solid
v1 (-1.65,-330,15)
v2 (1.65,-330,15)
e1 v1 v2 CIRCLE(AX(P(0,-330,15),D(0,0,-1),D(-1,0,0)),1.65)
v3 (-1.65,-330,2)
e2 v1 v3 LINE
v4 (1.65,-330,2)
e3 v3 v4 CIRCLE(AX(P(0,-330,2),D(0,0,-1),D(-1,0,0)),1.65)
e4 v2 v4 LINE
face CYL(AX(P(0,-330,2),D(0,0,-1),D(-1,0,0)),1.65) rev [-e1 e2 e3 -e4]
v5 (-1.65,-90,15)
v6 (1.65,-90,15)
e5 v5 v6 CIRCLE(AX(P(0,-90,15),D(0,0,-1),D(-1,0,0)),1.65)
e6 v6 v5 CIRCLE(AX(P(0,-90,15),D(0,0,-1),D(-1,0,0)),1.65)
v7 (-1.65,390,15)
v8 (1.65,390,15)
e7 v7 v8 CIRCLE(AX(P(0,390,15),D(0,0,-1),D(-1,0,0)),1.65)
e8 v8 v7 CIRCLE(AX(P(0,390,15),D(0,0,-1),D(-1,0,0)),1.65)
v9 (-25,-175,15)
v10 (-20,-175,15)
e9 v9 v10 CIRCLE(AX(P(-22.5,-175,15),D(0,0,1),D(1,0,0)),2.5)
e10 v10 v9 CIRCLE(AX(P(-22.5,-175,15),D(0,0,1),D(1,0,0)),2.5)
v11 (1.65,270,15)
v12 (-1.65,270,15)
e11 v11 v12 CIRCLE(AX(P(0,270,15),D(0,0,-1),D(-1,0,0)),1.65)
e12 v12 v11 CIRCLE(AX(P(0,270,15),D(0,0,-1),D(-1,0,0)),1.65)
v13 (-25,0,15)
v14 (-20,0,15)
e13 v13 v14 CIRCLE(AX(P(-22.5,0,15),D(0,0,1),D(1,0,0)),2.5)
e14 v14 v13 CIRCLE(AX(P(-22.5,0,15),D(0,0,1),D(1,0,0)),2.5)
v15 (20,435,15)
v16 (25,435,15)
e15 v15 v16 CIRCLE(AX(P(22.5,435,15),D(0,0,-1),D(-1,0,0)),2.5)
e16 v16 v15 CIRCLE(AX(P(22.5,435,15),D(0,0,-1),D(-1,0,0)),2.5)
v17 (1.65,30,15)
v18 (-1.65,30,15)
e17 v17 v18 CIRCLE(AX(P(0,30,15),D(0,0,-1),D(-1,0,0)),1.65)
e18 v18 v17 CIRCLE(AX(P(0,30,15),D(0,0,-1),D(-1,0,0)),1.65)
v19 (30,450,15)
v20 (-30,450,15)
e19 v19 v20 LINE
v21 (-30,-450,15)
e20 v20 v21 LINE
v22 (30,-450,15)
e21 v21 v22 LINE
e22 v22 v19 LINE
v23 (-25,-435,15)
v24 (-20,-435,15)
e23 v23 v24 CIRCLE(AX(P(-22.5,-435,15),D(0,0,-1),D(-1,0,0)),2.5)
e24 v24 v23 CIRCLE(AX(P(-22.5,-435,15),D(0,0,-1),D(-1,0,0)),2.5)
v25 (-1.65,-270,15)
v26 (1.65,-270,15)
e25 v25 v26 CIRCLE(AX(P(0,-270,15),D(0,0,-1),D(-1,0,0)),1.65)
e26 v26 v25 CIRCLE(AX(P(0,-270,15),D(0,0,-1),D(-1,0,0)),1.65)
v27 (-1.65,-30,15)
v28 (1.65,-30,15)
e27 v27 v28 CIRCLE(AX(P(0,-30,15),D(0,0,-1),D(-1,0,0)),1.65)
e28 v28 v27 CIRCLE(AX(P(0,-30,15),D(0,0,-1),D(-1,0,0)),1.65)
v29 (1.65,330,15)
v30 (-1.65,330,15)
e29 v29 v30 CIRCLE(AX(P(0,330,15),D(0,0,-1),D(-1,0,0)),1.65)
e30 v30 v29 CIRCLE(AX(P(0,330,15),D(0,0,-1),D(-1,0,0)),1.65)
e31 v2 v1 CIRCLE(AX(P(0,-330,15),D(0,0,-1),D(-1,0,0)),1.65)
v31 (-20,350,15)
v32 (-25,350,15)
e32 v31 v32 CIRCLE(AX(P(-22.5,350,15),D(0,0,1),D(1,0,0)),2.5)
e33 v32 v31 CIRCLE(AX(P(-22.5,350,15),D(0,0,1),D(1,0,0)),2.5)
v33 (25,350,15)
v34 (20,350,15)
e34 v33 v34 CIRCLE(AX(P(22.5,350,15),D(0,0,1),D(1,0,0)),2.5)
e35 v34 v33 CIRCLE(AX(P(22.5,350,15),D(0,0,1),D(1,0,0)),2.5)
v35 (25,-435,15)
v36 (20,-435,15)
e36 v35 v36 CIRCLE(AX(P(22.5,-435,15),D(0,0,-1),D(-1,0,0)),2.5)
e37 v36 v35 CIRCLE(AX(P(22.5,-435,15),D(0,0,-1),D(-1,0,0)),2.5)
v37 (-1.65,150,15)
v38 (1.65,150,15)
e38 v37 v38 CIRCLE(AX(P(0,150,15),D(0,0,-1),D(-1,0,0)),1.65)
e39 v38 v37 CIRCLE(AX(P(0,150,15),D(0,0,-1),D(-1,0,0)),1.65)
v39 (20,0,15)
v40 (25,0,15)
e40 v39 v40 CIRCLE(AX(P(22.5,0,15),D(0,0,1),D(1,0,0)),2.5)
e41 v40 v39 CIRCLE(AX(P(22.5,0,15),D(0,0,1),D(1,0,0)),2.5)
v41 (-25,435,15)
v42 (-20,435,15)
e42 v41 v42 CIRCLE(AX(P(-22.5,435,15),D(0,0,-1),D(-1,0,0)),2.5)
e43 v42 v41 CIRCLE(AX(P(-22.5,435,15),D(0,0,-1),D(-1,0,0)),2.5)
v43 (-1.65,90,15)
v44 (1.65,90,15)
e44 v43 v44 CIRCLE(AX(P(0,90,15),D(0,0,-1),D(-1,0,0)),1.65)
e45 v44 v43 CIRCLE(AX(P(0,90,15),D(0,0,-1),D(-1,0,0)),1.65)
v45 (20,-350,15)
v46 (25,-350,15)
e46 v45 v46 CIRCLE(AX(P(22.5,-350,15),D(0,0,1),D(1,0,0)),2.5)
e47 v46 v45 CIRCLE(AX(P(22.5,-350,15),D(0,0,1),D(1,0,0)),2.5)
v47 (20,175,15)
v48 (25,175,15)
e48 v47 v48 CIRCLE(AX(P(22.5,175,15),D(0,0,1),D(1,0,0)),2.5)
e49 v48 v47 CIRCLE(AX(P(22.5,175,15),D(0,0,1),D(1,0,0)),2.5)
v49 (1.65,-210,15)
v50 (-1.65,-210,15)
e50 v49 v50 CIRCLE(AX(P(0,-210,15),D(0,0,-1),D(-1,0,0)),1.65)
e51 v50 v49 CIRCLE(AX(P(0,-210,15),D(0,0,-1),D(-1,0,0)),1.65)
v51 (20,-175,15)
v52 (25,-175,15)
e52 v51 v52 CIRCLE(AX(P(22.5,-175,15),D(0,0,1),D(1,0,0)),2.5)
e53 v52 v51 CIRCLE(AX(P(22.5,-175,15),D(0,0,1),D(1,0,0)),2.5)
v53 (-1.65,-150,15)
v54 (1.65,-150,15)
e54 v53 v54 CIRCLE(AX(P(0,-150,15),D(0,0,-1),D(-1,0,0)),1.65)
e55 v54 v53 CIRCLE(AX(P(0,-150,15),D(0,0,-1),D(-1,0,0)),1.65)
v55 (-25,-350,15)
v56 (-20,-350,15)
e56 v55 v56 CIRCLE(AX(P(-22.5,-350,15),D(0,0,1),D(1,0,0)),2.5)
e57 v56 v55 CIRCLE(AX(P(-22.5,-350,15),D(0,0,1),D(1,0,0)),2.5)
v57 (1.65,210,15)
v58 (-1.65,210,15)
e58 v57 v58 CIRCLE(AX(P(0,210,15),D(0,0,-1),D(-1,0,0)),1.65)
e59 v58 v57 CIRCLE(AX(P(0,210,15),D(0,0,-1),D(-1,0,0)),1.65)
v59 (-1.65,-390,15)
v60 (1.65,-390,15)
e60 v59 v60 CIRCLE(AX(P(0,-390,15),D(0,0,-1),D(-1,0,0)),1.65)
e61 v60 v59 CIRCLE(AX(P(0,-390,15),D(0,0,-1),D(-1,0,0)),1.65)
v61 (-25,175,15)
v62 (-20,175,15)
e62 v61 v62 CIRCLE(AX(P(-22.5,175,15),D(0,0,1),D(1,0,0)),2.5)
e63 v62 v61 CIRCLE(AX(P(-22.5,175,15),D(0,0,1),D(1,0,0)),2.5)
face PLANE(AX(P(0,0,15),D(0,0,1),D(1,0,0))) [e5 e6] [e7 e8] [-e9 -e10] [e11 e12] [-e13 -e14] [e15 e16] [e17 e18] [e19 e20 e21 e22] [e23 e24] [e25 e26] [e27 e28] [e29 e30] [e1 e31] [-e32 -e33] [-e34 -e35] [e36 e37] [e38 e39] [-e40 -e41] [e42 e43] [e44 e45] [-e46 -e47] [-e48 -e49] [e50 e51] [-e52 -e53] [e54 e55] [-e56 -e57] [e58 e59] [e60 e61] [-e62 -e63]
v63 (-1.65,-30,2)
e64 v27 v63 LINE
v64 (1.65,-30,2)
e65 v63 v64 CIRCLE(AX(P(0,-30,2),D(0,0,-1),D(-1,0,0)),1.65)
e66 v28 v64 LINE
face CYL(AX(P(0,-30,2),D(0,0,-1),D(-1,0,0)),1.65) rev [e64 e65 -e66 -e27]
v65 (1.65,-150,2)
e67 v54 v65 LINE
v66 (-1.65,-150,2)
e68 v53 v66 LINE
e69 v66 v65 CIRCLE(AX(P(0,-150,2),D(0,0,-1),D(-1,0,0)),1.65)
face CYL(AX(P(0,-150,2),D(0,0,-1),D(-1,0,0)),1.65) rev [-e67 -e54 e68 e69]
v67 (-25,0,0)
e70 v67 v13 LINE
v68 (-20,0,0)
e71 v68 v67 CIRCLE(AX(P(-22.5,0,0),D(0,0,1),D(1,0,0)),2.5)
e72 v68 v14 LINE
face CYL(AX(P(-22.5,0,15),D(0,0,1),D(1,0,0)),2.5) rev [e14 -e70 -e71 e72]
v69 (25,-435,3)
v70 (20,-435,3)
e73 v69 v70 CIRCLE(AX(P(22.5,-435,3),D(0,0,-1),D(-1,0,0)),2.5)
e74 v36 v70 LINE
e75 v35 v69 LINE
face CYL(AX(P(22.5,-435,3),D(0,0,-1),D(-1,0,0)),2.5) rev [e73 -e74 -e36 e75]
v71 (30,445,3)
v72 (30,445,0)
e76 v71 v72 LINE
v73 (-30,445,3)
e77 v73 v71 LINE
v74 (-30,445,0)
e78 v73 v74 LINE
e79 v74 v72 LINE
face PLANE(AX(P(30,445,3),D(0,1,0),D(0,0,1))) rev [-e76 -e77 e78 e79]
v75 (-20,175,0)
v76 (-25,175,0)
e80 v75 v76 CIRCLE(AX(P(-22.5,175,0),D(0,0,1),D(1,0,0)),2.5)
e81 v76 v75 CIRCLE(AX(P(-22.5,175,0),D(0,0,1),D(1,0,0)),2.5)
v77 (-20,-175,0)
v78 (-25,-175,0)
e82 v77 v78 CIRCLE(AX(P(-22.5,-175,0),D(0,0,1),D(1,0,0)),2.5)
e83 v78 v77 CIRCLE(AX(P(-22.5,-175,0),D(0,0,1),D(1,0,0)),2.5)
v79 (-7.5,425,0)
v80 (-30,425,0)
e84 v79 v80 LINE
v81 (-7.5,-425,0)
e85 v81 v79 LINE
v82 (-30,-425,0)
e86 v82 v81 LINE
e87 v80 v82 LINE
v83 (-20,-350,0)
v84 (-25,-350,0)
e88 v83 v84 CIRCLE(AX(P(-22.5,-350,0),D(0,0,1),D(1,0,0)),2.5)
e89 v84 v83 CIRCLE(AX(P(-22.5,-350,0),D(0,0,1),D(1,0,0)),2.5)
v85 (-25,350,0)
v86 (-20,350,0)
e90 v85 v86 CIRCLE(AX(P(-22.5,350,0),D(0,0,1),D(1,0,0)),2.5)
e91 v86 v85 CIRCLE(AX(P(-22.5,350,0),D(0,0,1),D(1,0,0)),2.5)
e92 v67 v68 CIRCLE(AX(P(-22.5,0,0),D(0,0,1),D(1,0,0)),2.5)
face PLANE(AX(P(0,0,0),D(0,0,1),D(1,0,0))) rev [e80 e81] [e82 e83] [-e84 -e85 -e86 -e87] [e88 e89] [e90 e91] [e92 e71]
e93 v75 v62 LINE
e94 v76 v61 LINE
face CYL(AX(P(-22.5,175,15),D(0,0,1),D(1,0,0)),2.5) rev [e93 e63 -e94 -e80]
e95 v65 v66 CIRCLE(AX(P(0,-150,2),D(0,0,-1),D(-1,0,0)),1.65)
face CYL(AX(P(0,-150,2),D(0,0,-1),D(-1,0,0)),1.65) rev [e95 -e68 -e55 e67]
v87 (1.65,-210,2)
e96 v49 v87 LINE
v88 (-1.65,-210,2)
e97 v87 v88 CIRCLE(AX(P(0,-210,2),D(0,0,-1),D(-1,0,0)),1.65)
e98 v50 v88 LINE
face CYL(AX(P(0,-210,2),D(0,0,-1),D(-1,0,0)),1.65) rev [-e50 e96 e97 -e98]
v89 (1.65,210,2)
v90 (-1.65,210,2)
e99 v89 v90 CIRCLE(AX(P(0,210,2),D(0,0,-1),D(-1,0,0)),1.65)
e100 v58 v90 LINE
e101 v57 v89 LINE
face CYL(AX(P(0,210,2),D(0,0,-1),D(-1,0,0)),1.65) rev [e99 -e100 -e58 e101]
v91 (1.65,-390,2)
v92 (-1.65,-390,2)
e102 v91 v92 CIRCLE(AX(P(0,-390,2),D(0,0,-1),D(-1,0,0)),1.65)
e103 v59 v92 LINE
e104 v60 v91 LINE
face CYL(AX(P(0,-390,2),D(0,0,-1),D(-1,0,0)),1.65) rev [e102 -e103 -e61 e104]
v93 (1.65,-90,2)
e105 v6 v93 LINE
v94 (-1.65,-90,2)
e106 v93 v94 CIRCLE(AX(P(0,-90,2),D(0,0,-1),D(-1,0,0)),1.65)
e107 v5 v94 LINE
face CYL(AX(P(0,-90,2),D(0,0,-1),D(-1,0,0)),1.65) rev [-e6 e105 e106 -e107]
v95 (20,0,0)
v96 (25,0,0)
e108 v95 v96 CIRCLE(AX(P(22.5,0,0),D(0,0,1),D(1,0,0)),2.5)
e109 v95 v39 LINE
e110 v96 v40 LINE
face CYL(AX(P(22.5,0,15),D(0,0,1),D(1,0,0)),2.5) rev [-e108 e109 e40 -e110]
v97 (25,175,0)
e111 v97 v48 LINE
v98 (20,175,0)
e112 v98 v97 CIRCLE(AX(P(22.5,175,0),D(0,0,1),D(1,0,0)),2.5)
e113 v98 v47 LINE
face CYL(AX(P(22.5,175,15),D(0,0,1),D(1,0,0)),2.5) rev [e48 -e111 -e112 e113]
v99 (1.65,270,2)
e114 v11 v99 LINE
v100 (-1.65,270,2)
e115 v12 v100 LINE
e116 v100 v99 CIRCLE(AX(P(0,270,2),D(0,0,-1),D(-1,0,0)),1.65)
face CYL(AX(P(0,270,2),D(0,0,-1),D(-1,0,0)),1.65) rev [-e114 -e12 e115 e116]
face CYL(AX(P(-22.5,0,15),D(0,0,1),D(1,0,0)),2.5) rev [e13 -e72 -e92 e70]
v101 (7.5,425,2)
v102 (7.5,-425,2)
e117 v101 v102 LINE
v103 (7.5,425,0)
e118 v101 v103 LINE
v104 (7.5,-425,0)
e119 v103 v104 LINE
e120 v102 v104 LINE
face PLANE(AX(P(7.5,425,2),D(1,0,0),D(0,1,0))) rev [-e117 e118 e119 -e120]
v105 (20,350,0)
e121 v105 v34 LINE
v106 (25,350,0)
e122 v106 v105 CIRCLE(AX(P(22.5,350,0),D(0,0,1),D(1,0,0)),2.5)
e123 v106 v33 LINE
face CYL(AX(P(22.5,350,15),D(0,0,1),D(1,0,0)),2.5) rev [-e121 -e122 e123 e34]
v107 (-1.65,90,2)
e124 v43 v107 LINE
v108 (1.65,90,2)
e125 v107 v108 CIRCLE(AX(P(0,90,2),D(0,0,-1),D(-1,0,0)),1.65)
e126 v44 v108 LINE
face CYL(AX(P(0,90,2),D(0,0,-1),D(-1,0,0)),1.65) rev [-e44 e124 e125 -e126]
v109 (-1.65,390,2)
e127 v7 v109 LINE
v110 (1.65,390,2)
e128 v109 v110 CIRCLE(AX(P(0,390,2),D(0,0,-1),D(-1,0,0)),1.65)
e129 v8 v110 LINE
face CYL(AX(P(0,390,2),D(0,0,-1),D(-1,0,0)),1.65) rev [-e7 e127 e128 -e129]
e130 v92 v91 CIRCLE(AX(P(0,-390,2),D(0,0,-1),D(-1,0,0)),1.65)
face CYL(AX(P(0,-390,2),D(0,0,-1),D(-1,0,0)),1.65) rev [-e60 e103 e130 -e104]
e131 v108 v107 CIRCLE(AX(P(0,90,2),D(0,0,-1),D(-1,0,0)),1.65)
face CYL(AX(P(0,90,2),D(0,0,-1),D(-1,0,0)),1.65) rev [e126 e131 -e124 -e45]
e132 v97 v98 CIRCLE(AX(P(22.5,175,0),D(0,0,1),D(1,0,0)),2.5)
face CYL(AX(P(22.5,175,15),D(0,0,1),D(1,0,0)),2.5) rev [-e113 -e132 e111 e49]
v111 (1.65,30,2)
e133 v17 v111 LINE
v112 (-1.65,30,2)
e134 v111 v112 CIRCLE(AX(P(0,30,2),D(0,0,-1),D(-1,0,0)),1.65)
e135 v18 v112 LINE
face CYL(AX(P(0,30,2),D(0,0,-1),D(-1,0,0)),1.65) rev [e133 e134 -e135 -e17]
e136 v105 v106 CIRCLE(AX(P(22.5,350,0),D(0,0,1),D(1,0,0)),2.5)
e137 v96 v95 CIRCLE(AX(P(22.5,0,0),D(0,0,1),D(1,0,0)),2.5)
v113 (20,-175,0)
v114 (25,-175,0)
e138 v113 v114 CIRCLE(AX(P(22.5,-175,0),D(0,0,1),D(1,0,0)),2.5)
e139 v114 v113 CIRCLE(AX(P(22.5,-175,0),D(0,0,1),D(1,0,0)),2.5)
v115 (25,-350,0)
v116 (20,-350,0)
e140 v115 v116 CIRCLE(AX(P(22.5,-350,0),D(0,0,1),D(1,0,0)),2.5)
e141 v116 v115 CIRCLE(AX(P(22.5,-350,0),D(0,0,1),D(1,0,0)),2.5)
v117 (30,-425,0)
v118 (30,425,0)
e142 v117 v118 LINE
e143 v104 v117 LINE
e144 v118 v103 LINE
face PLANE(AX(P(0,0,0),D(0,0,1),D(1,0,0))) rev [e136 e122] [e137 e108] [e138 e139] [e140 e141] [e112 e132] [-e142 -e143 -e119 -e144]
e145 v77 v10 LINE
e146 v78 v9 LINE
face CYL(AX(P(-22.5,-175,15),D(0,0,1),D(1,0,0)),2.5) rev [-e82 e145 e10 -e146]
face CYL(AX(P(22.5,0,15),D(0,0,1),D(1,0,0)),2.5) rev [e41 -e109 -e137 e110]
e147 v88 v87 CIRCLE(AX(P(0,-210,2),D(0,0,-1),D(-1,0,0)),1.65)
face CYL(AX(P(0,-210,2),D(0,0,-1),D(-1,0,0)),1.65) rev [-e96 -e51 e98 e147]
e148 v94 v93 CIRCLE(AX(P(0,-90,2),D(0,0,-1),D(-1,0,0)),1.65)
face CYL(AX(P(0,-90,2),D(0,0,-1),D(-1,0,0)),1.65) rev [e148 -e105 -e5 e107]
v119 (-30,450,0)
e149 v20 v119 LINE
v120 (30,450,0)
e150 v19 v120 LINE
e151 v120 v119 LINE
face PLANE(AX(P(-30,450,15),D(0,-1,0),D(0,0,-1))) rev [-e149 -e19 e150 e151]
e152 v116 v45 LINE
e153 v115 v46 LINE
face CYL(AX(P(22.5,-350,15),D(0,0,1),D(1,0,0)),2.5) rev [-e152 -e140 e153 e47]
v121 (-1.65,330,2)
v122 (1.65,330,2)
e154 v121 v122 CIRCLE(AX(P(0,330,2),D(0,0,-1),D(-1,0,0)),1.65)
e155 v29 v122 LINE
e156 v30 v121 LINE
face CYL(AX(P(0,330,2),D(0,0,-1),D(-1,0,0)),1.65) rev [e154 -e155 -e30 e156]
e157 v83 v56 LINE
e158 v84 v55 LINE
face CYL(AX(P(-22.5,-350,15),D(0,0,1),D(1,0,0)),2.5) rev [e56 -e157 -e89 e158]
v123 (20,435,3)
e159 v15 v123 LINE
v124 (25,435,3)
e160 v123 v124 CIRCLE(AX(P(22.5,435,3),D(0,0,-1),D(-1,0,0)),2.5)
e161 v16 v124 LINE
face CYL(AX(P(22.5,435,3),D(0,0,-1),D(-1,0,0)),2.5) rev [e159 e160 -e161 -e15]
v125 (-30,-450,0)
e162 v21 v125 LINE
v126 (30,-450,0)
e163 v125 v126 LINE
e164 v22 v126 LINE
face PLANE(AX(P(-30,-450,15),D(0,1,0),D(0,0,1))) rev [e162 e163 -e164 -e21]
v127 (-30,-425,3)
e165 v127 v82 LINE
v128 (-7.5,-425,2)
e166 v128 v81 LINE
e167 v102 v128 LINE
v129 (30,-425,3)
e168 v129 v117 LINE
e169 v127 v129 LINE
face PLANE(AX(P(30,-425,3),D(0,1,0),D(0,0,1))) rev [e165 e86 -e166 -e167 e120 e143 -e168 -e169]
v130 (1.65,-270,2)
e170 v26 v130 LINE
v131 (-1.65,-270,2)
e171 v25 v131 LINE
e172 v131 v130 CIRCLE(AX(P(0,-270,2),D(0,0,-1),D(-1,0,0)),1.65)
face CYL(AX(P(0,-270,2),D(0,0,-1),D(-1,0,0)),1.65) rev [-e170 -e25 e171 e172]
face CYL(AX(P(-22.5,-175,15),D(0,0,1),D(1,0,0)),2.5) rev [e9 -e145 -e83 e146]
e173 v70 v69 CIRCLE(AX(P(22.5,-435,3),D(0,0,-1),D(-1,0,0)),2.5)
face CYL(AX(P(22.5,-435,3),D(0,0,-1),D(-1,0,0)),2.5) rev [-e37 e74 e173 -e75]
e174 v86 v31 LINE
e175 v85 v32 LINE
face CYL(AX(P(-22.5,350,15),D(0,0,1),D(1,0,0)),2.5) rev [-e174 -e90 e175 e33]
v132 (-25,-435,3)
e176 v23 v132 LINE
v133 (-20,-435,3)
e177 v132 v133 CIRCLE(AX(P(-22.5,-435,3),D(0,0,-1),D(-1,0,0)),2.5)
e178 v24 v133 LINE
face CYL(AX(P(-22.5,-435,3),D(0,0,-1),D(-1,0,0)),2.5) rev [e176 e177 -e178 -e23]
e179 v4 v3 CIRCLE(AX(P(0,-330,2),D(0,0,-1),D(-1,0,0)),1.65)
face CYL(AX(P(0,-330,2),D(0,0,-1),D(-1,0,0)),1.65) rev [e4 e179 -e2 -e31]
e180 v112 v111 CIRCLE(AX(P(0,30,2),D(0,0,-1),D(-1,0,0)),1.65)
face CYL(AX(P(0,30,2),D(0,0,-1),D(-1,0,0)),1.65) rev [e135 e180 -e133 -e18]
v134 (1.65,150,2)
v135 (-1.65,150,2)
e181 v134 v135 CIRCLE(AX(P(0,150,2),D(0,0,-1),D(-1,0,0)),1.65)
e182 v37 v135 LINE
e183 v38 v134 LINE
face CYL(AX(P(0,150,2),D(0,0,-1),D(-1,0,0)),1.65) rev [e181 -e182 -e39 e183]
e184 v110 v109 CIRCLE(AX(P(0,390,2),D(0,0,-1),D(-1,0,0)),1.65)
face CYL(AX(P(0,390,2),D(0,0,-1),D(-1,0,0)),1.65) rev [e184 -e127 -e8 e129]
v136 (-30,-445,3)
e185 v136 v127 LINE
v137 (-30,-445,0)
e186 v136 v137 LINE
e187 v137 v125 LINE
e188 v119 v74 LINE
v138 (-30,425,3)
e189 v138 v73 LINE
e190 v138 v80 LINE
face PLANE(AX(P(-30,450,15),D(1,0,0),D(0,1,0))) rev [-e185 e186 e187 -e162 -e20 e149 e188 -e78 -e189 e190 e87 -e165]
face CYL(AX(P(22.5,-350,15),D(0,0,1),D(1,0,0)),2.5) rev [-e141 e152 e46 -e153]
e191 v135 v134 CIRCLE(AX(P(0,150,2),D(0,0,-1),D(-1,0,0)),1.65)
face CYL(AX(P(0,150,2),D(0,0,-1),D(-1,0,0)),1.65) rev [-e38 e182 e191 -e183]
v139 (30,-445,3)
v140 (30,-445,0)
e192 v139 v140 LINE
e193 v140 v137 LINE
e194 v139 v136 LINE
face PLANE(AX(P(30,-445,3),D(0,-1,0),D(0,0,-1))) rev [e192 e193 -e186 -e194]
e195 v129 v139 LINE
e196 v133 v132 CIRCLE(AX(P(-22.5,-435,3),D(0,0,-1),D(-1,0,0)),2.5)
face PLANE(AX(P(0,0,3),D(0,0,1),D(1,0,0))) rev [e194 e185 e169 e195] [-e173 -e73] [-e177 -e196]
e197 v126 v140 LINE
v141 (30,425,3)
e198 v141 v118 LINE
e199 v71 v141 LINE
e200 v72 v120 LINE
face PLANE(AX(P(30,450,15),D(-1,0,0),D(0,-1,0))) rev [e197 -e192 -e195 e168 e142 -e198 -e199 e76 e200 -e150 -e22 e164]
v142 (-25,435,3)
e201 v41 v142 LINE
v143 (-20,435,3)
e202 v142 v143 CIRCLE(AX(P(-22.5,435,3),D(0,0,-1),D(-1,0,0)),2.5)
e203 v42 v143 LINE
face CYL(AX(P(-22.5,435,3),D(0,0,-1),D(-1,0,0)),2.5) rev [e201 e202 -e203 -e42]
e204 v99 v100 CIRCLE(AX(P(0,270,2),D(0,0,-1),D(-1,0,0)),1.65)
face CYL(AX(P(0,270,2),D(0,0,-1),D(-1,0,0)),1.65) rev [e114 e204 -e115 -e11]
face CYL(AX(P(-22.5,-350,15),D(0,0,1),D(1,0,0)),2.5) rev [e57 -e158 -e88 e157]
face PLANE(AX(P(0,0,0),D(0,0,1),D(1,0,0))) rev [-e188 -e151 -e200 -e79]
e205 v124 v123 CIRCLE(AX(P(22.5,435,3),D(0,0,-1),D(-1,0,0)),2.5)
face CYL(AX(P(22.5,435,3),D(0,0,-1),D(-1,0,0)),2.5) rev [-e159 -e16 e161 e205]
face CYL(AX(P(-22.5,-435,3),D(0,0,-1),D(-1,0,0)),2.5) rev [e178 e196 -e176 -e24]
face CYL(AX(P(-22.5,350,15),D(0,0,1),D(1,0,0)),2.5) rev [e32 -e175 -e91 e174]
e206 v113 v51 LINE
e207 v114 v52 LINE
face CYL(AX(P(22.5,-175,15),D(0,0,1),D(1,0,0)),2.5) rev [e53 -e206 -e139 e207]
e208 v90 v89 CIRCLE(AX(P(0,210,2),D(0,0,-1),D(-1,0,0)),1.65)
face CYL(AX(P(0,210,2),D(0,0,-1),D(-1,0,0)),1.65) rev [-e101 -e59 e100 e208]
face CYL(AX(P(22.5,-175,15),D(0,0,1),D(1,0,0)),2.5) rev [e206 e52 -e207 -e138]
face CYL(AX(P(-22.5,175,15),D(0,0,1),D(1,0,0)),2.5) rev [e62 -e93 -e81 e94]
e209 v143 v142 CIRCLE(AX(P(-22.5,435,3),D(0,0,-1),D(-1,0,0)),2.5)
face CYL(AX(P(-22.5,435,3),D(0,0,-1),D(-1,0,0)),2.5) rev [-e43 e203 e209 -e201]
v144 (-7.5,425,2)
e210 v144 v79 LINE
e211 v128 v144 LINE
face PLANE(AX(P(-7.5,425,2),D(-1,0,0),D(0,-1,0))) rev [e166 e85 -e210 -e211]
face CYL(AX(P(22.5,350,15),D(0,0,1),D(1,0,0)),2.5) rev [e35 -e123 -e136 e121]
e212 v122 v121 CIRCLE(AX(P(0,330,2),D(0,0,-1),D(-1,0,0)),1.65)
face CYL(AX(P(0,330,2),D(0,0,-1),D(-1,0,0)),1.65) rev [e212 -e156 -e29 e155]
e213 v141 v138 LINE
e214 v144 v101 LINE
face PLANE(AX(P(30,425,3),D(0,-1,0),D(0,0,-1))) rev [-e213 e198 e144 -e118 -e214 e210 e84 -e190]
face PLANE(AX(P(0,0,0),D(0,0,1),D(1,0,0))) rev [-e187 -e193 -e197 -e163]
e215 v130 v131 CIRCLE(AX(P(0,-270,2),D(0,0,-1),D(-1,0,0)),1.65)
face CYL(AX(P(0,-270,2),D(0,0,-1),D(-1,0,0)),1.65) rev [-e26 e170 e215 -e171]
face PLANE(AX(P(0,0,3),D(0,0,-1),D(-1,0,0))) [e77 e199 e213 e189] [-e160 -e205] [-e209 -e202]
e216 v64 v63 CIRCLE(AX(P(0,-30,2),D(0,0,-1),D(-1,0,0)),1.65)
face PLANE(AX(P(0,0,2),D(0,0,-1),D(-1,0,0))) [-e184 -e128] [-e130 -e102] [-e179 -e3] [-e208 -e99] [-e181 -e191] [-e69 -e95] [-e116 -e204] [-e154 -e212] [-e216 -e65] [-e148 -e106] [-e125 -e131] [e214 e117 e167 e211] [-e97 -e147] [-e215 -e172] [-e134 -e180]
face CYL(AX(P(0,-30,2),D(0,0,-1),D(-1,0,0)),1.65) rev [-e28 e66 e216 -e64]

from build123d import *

# Parameters (mm, degrees)
SKETCH1_W           = 60
SKETCH1_H           = 900
BOSS_EXTRUDE1_DEPTH = 15
SKETCH5_W           = 60
SKETCH5_H           = 20
CUT_EXTRUDE2_DEPTH  = 3
SKETCH7_W           = 15
SKETCH7_H           = 850
CUT_EXTRUDE3_DEPTH  = 2
M4_TAPPED_HOLE1_D   = 3.3
LPATTERN1_COUNT     = 14
LPATTERN1_PITCH     = 60
M6_TAPPED_HOLE1_D   = 5
M6_TAPPED_HOLE2_D   = 5
LPATTERN2_COUNT     = 3
LPATTERN2_PITCH     = 175
LPATTERN2_COL_COUNT = 3
LPATTERN2_COL_PITCH = 175


with BuildPart() as part:
    # Sketch1 → Boss-Extrude1 (new body)
    with BuildSketch(Plane.XY):
        Rectangle(SKETCH1_W, SKETCH1_H)
    extrude(amount=BOSS_EXTRUDE1_DEPTH)

    # Sketch5 → Cut-Extrude2 (cut)
    with BuildSketch(Plane(origin=(0, 0, 0), x_dir=(-1, 0, 0), z_dir=(0, 0, -1))):
        with Locations((0, 435)):
            Rectangle(SKETCH5_W, SKETCH5_H)
        with Locations((0, -435)):
            Rectangle(SKETCH5_W, SKETCH5_H)
    extrude(amount=-CUT_EXTRUDE2_DEPTH, mode=Mode.SUBTRACT)

    # Sketch7 → Cut-Extrude3 (cut)
    with BuildSketch(Plane(origin=(0, 0, 0), x_dir=(-1, 0, 0), z_dir=(0, 0, -1))):
        Rectangle(SKETCH7_W, SKETCH7_H)
    extrude(amount=-CUT_EXTRUDE3_DEPTH, mode=Mode.SUBTRACT)

    # M4 Tapped Hole1 (through all)
    with Locations(Plane(origin=(0, 0, 2), x_dir=(-1, 0, 0), z_dir=(0, 0, -1))):
        with Locations((0, 390)):
            m4_tapped_hole1 = Hole(M4_TAPPED_HOLE1_D / 2)

    # LPattern1: M4 Tapped Hole1 ×14
    with Locations(*[(0, -i * LPATTERN1_PITCH, 0) for i in range(1, LPATTERN1_COUNT)]):
        add(m4_tapped_hole1, mode=Mode.SUBTRACT)

    # M6 Tapped Hole1 (through all)
    with Locations(Plane(origin=(0, 0, 3), x_dir=(-1, 0, 0), z_dir=(0, 0, -1))):
        with Locations((-22.5, 435), (22.5, 435), (-22.5, -435), (22.5, -435)):
            Hole(M6_TAPPED_HOLE1_D / 2)

    # M6 Tapped Hole2 (through all)
    with Locations(Plane.XY.offset(15)):
        with Locations((-22.5, 0), (22.5, 0)):
            m6_tapped_hole2 = Hole(M6_TAPPED_HOLE2_D / 2)

    # LPattern2: M6 Tapped Hole2 ×3
    with Locations(*[(0, -i * LPATTERN2_PITCH, 0) for i in range(1, LPATTERN2_COUNT)]):
        add(m6_tapped_hole2, mode=Mode.SUBTRACT)

    # LPattern2 col: M6 Tapped Hole2 ×3
    with Locations(*[(0, i * LPATTERN2_COL_PITCH, 0) for i in range(1, LPATTERN2_COL_COUNT)]):
        add(m6_tapped_hole2, mode=Mode.SUBTRACT)


solid = part.part
